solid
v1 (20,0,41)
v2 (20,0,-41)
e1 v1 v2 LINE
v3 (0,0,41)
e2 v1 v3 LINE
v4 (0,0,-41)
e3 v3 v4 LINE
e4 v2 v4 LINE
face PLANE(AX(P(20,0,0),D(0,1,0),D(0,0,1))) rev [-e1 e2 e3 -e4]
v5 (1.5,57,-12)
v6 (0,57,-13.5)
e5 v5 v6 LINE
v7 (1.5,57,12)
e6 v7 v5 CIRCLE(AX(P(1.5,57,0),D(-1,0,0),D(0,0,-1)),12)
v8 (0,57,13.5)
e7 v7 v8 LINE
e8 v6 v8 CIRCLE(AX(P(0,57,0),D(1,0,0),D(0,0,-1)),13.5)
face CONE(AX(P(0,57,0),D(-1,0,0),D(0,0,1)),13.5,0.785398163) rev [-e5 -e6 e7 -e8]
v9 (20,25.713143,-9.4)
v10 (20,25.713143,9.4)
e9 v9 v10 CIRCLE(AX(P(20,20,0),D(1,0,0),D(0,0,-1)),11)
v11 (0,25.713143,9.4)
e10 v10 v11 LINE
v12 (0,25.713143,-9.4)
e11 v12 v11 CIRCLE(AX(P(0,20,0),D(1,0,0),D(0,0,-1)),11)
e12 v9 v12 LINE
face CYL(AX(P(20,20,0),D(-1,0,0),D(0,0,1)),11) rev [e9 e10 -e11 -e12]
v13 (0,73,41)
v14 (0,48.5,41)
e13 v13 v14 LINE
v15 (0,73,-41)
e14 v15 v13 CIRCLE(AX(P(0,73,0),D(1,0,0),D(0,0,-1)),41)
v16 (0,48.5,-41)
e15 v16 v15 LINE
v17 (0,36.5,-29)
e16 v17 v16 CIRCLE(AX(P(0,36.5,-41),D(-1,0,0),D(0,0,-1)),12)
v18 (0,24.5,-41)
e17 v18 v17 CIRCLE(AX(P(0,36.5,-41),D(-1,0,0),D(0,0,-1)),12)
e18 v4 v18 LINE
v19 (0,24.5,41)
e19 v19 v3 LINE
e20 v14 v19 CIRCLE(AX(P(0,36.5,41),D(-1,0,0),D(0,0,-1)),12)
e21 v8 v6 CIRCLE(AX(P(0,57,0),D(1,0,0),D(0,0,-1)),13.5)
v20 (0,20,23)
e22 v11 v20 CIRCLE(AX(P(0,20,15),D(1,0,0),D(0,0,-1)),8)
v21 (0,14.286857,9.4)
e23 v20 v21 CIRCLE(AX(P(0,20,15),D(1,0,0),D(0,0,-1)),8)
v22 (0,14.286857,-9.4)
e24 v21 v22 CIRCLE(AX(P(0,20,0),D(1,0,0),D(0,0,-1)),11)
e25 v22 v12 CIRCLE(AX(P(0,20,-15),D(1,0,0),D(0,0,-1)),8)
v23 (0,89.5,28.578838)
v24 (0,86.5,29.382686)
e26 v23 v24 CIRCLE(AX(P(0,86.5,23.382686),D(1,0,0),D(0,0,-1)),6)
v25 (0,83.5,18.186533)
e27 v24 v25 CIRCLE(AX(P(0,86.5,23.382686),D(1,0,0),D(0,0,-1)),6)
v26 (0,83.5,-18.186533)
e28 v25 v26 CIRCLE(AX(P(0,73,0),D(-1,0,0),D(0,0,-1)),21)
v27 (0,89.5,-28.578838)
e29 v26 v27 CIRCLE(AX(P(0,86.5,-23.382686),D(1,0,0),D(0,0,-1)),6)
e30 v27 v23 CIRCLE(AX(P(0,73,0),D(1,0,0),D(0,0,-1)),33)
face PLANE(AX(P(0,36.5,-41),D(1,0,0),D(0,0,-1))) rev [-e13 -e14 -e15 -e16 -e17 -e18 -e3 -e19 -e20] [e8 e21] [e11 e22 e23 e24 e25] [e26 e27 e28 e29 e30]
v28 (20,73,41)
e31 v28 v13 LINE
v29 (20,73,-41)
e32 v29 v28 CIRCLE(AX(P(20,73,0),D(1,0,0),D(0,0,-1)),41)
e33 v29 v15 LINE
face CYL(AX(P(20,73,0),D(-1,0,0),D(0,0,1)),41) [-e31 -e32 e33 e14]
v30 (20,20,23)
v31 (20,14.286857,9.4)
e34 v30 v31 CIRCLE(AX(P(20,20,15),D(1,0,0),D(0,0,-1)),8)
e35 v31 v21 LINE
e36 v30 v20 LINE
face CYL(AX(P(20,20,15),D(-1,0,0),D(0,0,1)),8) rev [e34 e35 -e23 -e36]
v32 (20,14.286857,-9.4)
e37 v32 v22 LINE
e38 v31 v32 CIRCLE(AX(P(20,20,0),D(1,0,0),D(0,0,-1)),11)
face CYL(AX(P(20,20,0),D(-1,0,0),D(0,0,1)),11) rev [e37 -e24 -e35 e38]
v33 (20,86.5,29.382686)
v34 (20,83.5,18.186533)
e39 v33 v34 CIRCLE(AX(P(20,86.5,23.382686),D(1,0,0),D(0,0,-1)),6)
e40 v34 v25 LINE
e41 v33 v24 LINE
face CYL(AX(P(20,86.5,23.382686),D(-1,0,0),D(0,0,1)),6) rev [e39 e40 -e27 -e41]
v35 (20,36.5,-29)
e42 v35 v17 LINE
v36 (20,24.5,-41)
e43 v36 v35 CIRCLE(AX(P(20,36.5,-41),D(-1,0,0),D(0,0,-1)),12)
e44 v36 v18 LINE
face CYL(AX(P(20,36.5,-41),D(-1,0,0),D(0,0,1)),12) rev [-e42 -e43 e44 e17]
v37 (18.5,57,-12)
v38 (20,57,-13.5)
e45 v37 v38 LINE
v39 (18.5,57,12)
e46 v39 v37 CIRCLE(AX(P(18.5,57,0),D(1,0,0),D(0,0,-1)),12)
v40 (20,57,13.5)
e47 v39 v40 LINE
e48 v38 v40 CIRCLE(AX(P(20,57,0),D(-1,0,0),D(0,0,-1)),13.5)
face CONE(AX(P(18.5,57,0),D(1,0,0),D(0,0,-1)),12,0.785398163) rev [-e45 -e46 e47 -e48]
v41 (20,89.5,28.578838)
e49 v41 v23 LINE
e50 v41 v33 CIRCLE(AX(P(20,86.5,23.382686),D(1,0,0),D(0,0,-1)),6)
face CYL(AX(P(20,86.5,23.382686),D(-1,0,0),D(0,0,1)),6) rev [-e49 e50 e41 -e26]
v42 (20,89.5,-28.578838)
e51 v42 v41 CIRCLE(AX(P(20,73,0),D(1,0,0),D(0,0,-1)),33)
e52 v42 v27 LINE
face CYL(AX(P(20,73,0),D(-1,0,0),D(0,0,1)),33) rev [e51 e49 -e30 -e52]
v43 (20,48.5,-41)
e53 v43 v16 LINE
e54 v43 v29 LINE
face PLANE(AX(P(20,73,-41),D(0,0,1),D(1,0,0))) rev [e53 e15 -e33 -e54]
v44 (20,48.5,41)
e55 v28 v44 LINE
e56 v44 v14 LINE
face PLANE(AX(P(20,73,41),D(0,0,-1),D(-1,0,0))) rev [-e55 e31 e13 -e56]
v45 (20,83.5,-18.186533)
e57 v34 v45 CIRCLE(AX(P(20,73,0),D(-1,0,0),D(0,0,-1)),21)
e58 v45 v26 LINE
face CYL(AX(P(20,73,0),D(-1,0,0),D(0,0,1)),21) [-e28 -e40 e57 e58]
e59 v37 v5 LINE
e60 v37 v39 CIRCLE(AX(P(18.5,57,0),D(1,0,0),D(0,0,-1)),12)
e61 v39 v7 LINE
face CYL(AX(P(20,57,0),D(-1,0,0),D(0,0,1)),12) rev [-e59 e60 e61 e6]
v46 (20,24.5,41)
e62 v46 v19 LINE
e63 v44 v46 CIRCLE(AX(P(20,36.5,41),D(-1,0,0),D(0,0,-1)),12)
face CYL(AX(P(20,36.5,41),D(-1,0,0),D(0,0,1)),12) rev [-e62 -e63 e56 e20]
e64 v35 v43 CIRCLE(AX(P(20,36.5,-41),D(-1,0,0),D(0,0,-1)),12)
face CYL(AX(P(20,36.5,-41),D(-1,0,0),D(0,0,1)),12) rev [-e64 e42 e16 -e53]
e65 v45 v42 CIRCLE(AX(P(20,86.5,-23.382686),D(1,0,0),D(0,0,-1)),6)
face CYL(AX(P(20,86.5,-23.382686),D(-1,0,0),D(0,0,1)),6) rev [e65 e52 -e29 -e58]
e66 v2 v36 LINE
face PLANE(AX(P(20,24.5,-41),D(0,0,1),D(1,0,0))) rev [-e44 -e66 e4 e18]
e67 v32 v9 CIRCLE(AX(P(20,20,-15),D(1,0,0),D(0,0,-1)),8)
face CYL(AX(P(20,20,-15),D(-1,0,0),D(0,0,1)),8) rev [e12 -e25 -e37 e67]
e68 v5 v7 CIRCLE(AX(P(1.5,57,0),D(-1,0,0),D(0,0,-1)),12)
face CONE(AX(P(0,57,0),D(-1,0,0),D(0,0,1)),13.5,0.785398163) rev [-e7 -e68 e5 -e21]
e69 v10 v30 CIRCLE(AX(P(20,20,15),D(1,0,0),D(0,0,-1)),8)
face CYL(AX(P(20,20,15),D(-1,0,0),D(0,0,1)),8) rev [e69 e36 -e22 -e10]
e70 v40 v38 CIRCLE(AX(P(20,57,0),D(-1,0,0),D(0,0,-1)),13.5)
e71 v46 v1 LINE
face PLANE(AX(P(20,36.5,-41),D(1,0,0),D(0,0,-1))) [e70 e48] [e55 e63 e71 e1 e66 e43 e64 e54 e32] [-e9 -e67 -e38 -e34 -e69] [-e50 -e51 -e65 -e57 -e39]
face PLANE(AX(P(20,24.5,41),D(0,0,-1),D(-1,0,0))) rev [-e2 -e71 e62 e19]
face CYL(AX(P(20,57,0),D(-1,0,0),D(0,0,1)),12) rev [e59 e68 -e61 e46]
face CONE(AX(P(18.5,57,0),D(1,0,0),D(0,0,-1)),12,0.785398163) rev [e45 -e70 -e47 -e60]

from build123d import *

# Parameters (mm, degrees)
PLATE_PROFILE_SKETCH_R      = 12
PROFILED_PLATE_20MM_DEPTH   = 20
BORE_CHAMFER_1_5X45DEG_SIZE = 1.5


with BuildPart() as part:
    # Plate Profile Sketch → Profiled Plate 20mm (new body)
    with BuildSketch(Plane(origin=(0, 0, 0), x_dir=(0, 0, -1), z_dir=(1, 0, 0))):
        with BuildLine():
            Line((41, 73), (41, 48.5))
            ThreePointArc((41, 48.5), (29, 36.5), (41, 24.5))
            Line((41, 24.5), (41, 0))
            Line((41, 0), (0, 0))
            Line((0, 0), (-41, 0))
            Line((-41, 0), (-41, 24.5))
            ThreePointArc((-41, 24.5), (-29, 36.5), (-41, 48.5))
            Line((-41, 48.5), (-41, 73))
            ThreePointArc((-41, 73), (0, 114), (41, 73))
        make_face()
        with Locations((0, 57)):
            Circle(PLATE_PROFILE_SKETCH_R, mode=Mode.SUBTRACT)
        with BuildLine():
            ThreePointArc((9.4, 25.713142743), (0, 31), (-9.4, 25.713142743))
            ThreePointArc((-9.4, 25.713142743), (-23, 20), (-9.4, 14.286857257))
            ThreePointArc((-9.4, 14.286857257), (0, 9), (9.4, 14.286857257))
            ThreePointArc((9.4, 14.286857257), (23, 20), (9.4, 25.713142743))
        make_face(mode=Mode.SUBTRACT)
        with BuildLine():
            ThreePointArc((28.578838325, 89.5), (0, 106), (-28.578838325, 89.5))
            ThreePointArc((-28.578838325, 89.5), (-26.382685902, 81.303847577), (-18.186533479, 83.5))
            ThreePointArc((-18.186533479, 83.5), (0, 94), (18.186533479, 83.5))
            ThreePointArc((18.186533479, 83.5), (26.382685902, 81.303847577), (28.578838325, 89.5))
        make_face(mode=Mode.SUBTRACT)
    extrude(amount=PROFILED_PLATE_20MM_DEPTH)

    # Bore Chamfer 1.5x45deg
    bore_chamfer_1_5x45deg_edges = [part.edges().sort_by_distance(p)[0] for p in [
        (0, 57, 12),
        (20, 57, 12),
    ]]
    chamfer(bore_chamfer_1_5x45deg_edges, length=BORE_CHAMFER_1_5X45DEG_SIZE)


solid = part.part
